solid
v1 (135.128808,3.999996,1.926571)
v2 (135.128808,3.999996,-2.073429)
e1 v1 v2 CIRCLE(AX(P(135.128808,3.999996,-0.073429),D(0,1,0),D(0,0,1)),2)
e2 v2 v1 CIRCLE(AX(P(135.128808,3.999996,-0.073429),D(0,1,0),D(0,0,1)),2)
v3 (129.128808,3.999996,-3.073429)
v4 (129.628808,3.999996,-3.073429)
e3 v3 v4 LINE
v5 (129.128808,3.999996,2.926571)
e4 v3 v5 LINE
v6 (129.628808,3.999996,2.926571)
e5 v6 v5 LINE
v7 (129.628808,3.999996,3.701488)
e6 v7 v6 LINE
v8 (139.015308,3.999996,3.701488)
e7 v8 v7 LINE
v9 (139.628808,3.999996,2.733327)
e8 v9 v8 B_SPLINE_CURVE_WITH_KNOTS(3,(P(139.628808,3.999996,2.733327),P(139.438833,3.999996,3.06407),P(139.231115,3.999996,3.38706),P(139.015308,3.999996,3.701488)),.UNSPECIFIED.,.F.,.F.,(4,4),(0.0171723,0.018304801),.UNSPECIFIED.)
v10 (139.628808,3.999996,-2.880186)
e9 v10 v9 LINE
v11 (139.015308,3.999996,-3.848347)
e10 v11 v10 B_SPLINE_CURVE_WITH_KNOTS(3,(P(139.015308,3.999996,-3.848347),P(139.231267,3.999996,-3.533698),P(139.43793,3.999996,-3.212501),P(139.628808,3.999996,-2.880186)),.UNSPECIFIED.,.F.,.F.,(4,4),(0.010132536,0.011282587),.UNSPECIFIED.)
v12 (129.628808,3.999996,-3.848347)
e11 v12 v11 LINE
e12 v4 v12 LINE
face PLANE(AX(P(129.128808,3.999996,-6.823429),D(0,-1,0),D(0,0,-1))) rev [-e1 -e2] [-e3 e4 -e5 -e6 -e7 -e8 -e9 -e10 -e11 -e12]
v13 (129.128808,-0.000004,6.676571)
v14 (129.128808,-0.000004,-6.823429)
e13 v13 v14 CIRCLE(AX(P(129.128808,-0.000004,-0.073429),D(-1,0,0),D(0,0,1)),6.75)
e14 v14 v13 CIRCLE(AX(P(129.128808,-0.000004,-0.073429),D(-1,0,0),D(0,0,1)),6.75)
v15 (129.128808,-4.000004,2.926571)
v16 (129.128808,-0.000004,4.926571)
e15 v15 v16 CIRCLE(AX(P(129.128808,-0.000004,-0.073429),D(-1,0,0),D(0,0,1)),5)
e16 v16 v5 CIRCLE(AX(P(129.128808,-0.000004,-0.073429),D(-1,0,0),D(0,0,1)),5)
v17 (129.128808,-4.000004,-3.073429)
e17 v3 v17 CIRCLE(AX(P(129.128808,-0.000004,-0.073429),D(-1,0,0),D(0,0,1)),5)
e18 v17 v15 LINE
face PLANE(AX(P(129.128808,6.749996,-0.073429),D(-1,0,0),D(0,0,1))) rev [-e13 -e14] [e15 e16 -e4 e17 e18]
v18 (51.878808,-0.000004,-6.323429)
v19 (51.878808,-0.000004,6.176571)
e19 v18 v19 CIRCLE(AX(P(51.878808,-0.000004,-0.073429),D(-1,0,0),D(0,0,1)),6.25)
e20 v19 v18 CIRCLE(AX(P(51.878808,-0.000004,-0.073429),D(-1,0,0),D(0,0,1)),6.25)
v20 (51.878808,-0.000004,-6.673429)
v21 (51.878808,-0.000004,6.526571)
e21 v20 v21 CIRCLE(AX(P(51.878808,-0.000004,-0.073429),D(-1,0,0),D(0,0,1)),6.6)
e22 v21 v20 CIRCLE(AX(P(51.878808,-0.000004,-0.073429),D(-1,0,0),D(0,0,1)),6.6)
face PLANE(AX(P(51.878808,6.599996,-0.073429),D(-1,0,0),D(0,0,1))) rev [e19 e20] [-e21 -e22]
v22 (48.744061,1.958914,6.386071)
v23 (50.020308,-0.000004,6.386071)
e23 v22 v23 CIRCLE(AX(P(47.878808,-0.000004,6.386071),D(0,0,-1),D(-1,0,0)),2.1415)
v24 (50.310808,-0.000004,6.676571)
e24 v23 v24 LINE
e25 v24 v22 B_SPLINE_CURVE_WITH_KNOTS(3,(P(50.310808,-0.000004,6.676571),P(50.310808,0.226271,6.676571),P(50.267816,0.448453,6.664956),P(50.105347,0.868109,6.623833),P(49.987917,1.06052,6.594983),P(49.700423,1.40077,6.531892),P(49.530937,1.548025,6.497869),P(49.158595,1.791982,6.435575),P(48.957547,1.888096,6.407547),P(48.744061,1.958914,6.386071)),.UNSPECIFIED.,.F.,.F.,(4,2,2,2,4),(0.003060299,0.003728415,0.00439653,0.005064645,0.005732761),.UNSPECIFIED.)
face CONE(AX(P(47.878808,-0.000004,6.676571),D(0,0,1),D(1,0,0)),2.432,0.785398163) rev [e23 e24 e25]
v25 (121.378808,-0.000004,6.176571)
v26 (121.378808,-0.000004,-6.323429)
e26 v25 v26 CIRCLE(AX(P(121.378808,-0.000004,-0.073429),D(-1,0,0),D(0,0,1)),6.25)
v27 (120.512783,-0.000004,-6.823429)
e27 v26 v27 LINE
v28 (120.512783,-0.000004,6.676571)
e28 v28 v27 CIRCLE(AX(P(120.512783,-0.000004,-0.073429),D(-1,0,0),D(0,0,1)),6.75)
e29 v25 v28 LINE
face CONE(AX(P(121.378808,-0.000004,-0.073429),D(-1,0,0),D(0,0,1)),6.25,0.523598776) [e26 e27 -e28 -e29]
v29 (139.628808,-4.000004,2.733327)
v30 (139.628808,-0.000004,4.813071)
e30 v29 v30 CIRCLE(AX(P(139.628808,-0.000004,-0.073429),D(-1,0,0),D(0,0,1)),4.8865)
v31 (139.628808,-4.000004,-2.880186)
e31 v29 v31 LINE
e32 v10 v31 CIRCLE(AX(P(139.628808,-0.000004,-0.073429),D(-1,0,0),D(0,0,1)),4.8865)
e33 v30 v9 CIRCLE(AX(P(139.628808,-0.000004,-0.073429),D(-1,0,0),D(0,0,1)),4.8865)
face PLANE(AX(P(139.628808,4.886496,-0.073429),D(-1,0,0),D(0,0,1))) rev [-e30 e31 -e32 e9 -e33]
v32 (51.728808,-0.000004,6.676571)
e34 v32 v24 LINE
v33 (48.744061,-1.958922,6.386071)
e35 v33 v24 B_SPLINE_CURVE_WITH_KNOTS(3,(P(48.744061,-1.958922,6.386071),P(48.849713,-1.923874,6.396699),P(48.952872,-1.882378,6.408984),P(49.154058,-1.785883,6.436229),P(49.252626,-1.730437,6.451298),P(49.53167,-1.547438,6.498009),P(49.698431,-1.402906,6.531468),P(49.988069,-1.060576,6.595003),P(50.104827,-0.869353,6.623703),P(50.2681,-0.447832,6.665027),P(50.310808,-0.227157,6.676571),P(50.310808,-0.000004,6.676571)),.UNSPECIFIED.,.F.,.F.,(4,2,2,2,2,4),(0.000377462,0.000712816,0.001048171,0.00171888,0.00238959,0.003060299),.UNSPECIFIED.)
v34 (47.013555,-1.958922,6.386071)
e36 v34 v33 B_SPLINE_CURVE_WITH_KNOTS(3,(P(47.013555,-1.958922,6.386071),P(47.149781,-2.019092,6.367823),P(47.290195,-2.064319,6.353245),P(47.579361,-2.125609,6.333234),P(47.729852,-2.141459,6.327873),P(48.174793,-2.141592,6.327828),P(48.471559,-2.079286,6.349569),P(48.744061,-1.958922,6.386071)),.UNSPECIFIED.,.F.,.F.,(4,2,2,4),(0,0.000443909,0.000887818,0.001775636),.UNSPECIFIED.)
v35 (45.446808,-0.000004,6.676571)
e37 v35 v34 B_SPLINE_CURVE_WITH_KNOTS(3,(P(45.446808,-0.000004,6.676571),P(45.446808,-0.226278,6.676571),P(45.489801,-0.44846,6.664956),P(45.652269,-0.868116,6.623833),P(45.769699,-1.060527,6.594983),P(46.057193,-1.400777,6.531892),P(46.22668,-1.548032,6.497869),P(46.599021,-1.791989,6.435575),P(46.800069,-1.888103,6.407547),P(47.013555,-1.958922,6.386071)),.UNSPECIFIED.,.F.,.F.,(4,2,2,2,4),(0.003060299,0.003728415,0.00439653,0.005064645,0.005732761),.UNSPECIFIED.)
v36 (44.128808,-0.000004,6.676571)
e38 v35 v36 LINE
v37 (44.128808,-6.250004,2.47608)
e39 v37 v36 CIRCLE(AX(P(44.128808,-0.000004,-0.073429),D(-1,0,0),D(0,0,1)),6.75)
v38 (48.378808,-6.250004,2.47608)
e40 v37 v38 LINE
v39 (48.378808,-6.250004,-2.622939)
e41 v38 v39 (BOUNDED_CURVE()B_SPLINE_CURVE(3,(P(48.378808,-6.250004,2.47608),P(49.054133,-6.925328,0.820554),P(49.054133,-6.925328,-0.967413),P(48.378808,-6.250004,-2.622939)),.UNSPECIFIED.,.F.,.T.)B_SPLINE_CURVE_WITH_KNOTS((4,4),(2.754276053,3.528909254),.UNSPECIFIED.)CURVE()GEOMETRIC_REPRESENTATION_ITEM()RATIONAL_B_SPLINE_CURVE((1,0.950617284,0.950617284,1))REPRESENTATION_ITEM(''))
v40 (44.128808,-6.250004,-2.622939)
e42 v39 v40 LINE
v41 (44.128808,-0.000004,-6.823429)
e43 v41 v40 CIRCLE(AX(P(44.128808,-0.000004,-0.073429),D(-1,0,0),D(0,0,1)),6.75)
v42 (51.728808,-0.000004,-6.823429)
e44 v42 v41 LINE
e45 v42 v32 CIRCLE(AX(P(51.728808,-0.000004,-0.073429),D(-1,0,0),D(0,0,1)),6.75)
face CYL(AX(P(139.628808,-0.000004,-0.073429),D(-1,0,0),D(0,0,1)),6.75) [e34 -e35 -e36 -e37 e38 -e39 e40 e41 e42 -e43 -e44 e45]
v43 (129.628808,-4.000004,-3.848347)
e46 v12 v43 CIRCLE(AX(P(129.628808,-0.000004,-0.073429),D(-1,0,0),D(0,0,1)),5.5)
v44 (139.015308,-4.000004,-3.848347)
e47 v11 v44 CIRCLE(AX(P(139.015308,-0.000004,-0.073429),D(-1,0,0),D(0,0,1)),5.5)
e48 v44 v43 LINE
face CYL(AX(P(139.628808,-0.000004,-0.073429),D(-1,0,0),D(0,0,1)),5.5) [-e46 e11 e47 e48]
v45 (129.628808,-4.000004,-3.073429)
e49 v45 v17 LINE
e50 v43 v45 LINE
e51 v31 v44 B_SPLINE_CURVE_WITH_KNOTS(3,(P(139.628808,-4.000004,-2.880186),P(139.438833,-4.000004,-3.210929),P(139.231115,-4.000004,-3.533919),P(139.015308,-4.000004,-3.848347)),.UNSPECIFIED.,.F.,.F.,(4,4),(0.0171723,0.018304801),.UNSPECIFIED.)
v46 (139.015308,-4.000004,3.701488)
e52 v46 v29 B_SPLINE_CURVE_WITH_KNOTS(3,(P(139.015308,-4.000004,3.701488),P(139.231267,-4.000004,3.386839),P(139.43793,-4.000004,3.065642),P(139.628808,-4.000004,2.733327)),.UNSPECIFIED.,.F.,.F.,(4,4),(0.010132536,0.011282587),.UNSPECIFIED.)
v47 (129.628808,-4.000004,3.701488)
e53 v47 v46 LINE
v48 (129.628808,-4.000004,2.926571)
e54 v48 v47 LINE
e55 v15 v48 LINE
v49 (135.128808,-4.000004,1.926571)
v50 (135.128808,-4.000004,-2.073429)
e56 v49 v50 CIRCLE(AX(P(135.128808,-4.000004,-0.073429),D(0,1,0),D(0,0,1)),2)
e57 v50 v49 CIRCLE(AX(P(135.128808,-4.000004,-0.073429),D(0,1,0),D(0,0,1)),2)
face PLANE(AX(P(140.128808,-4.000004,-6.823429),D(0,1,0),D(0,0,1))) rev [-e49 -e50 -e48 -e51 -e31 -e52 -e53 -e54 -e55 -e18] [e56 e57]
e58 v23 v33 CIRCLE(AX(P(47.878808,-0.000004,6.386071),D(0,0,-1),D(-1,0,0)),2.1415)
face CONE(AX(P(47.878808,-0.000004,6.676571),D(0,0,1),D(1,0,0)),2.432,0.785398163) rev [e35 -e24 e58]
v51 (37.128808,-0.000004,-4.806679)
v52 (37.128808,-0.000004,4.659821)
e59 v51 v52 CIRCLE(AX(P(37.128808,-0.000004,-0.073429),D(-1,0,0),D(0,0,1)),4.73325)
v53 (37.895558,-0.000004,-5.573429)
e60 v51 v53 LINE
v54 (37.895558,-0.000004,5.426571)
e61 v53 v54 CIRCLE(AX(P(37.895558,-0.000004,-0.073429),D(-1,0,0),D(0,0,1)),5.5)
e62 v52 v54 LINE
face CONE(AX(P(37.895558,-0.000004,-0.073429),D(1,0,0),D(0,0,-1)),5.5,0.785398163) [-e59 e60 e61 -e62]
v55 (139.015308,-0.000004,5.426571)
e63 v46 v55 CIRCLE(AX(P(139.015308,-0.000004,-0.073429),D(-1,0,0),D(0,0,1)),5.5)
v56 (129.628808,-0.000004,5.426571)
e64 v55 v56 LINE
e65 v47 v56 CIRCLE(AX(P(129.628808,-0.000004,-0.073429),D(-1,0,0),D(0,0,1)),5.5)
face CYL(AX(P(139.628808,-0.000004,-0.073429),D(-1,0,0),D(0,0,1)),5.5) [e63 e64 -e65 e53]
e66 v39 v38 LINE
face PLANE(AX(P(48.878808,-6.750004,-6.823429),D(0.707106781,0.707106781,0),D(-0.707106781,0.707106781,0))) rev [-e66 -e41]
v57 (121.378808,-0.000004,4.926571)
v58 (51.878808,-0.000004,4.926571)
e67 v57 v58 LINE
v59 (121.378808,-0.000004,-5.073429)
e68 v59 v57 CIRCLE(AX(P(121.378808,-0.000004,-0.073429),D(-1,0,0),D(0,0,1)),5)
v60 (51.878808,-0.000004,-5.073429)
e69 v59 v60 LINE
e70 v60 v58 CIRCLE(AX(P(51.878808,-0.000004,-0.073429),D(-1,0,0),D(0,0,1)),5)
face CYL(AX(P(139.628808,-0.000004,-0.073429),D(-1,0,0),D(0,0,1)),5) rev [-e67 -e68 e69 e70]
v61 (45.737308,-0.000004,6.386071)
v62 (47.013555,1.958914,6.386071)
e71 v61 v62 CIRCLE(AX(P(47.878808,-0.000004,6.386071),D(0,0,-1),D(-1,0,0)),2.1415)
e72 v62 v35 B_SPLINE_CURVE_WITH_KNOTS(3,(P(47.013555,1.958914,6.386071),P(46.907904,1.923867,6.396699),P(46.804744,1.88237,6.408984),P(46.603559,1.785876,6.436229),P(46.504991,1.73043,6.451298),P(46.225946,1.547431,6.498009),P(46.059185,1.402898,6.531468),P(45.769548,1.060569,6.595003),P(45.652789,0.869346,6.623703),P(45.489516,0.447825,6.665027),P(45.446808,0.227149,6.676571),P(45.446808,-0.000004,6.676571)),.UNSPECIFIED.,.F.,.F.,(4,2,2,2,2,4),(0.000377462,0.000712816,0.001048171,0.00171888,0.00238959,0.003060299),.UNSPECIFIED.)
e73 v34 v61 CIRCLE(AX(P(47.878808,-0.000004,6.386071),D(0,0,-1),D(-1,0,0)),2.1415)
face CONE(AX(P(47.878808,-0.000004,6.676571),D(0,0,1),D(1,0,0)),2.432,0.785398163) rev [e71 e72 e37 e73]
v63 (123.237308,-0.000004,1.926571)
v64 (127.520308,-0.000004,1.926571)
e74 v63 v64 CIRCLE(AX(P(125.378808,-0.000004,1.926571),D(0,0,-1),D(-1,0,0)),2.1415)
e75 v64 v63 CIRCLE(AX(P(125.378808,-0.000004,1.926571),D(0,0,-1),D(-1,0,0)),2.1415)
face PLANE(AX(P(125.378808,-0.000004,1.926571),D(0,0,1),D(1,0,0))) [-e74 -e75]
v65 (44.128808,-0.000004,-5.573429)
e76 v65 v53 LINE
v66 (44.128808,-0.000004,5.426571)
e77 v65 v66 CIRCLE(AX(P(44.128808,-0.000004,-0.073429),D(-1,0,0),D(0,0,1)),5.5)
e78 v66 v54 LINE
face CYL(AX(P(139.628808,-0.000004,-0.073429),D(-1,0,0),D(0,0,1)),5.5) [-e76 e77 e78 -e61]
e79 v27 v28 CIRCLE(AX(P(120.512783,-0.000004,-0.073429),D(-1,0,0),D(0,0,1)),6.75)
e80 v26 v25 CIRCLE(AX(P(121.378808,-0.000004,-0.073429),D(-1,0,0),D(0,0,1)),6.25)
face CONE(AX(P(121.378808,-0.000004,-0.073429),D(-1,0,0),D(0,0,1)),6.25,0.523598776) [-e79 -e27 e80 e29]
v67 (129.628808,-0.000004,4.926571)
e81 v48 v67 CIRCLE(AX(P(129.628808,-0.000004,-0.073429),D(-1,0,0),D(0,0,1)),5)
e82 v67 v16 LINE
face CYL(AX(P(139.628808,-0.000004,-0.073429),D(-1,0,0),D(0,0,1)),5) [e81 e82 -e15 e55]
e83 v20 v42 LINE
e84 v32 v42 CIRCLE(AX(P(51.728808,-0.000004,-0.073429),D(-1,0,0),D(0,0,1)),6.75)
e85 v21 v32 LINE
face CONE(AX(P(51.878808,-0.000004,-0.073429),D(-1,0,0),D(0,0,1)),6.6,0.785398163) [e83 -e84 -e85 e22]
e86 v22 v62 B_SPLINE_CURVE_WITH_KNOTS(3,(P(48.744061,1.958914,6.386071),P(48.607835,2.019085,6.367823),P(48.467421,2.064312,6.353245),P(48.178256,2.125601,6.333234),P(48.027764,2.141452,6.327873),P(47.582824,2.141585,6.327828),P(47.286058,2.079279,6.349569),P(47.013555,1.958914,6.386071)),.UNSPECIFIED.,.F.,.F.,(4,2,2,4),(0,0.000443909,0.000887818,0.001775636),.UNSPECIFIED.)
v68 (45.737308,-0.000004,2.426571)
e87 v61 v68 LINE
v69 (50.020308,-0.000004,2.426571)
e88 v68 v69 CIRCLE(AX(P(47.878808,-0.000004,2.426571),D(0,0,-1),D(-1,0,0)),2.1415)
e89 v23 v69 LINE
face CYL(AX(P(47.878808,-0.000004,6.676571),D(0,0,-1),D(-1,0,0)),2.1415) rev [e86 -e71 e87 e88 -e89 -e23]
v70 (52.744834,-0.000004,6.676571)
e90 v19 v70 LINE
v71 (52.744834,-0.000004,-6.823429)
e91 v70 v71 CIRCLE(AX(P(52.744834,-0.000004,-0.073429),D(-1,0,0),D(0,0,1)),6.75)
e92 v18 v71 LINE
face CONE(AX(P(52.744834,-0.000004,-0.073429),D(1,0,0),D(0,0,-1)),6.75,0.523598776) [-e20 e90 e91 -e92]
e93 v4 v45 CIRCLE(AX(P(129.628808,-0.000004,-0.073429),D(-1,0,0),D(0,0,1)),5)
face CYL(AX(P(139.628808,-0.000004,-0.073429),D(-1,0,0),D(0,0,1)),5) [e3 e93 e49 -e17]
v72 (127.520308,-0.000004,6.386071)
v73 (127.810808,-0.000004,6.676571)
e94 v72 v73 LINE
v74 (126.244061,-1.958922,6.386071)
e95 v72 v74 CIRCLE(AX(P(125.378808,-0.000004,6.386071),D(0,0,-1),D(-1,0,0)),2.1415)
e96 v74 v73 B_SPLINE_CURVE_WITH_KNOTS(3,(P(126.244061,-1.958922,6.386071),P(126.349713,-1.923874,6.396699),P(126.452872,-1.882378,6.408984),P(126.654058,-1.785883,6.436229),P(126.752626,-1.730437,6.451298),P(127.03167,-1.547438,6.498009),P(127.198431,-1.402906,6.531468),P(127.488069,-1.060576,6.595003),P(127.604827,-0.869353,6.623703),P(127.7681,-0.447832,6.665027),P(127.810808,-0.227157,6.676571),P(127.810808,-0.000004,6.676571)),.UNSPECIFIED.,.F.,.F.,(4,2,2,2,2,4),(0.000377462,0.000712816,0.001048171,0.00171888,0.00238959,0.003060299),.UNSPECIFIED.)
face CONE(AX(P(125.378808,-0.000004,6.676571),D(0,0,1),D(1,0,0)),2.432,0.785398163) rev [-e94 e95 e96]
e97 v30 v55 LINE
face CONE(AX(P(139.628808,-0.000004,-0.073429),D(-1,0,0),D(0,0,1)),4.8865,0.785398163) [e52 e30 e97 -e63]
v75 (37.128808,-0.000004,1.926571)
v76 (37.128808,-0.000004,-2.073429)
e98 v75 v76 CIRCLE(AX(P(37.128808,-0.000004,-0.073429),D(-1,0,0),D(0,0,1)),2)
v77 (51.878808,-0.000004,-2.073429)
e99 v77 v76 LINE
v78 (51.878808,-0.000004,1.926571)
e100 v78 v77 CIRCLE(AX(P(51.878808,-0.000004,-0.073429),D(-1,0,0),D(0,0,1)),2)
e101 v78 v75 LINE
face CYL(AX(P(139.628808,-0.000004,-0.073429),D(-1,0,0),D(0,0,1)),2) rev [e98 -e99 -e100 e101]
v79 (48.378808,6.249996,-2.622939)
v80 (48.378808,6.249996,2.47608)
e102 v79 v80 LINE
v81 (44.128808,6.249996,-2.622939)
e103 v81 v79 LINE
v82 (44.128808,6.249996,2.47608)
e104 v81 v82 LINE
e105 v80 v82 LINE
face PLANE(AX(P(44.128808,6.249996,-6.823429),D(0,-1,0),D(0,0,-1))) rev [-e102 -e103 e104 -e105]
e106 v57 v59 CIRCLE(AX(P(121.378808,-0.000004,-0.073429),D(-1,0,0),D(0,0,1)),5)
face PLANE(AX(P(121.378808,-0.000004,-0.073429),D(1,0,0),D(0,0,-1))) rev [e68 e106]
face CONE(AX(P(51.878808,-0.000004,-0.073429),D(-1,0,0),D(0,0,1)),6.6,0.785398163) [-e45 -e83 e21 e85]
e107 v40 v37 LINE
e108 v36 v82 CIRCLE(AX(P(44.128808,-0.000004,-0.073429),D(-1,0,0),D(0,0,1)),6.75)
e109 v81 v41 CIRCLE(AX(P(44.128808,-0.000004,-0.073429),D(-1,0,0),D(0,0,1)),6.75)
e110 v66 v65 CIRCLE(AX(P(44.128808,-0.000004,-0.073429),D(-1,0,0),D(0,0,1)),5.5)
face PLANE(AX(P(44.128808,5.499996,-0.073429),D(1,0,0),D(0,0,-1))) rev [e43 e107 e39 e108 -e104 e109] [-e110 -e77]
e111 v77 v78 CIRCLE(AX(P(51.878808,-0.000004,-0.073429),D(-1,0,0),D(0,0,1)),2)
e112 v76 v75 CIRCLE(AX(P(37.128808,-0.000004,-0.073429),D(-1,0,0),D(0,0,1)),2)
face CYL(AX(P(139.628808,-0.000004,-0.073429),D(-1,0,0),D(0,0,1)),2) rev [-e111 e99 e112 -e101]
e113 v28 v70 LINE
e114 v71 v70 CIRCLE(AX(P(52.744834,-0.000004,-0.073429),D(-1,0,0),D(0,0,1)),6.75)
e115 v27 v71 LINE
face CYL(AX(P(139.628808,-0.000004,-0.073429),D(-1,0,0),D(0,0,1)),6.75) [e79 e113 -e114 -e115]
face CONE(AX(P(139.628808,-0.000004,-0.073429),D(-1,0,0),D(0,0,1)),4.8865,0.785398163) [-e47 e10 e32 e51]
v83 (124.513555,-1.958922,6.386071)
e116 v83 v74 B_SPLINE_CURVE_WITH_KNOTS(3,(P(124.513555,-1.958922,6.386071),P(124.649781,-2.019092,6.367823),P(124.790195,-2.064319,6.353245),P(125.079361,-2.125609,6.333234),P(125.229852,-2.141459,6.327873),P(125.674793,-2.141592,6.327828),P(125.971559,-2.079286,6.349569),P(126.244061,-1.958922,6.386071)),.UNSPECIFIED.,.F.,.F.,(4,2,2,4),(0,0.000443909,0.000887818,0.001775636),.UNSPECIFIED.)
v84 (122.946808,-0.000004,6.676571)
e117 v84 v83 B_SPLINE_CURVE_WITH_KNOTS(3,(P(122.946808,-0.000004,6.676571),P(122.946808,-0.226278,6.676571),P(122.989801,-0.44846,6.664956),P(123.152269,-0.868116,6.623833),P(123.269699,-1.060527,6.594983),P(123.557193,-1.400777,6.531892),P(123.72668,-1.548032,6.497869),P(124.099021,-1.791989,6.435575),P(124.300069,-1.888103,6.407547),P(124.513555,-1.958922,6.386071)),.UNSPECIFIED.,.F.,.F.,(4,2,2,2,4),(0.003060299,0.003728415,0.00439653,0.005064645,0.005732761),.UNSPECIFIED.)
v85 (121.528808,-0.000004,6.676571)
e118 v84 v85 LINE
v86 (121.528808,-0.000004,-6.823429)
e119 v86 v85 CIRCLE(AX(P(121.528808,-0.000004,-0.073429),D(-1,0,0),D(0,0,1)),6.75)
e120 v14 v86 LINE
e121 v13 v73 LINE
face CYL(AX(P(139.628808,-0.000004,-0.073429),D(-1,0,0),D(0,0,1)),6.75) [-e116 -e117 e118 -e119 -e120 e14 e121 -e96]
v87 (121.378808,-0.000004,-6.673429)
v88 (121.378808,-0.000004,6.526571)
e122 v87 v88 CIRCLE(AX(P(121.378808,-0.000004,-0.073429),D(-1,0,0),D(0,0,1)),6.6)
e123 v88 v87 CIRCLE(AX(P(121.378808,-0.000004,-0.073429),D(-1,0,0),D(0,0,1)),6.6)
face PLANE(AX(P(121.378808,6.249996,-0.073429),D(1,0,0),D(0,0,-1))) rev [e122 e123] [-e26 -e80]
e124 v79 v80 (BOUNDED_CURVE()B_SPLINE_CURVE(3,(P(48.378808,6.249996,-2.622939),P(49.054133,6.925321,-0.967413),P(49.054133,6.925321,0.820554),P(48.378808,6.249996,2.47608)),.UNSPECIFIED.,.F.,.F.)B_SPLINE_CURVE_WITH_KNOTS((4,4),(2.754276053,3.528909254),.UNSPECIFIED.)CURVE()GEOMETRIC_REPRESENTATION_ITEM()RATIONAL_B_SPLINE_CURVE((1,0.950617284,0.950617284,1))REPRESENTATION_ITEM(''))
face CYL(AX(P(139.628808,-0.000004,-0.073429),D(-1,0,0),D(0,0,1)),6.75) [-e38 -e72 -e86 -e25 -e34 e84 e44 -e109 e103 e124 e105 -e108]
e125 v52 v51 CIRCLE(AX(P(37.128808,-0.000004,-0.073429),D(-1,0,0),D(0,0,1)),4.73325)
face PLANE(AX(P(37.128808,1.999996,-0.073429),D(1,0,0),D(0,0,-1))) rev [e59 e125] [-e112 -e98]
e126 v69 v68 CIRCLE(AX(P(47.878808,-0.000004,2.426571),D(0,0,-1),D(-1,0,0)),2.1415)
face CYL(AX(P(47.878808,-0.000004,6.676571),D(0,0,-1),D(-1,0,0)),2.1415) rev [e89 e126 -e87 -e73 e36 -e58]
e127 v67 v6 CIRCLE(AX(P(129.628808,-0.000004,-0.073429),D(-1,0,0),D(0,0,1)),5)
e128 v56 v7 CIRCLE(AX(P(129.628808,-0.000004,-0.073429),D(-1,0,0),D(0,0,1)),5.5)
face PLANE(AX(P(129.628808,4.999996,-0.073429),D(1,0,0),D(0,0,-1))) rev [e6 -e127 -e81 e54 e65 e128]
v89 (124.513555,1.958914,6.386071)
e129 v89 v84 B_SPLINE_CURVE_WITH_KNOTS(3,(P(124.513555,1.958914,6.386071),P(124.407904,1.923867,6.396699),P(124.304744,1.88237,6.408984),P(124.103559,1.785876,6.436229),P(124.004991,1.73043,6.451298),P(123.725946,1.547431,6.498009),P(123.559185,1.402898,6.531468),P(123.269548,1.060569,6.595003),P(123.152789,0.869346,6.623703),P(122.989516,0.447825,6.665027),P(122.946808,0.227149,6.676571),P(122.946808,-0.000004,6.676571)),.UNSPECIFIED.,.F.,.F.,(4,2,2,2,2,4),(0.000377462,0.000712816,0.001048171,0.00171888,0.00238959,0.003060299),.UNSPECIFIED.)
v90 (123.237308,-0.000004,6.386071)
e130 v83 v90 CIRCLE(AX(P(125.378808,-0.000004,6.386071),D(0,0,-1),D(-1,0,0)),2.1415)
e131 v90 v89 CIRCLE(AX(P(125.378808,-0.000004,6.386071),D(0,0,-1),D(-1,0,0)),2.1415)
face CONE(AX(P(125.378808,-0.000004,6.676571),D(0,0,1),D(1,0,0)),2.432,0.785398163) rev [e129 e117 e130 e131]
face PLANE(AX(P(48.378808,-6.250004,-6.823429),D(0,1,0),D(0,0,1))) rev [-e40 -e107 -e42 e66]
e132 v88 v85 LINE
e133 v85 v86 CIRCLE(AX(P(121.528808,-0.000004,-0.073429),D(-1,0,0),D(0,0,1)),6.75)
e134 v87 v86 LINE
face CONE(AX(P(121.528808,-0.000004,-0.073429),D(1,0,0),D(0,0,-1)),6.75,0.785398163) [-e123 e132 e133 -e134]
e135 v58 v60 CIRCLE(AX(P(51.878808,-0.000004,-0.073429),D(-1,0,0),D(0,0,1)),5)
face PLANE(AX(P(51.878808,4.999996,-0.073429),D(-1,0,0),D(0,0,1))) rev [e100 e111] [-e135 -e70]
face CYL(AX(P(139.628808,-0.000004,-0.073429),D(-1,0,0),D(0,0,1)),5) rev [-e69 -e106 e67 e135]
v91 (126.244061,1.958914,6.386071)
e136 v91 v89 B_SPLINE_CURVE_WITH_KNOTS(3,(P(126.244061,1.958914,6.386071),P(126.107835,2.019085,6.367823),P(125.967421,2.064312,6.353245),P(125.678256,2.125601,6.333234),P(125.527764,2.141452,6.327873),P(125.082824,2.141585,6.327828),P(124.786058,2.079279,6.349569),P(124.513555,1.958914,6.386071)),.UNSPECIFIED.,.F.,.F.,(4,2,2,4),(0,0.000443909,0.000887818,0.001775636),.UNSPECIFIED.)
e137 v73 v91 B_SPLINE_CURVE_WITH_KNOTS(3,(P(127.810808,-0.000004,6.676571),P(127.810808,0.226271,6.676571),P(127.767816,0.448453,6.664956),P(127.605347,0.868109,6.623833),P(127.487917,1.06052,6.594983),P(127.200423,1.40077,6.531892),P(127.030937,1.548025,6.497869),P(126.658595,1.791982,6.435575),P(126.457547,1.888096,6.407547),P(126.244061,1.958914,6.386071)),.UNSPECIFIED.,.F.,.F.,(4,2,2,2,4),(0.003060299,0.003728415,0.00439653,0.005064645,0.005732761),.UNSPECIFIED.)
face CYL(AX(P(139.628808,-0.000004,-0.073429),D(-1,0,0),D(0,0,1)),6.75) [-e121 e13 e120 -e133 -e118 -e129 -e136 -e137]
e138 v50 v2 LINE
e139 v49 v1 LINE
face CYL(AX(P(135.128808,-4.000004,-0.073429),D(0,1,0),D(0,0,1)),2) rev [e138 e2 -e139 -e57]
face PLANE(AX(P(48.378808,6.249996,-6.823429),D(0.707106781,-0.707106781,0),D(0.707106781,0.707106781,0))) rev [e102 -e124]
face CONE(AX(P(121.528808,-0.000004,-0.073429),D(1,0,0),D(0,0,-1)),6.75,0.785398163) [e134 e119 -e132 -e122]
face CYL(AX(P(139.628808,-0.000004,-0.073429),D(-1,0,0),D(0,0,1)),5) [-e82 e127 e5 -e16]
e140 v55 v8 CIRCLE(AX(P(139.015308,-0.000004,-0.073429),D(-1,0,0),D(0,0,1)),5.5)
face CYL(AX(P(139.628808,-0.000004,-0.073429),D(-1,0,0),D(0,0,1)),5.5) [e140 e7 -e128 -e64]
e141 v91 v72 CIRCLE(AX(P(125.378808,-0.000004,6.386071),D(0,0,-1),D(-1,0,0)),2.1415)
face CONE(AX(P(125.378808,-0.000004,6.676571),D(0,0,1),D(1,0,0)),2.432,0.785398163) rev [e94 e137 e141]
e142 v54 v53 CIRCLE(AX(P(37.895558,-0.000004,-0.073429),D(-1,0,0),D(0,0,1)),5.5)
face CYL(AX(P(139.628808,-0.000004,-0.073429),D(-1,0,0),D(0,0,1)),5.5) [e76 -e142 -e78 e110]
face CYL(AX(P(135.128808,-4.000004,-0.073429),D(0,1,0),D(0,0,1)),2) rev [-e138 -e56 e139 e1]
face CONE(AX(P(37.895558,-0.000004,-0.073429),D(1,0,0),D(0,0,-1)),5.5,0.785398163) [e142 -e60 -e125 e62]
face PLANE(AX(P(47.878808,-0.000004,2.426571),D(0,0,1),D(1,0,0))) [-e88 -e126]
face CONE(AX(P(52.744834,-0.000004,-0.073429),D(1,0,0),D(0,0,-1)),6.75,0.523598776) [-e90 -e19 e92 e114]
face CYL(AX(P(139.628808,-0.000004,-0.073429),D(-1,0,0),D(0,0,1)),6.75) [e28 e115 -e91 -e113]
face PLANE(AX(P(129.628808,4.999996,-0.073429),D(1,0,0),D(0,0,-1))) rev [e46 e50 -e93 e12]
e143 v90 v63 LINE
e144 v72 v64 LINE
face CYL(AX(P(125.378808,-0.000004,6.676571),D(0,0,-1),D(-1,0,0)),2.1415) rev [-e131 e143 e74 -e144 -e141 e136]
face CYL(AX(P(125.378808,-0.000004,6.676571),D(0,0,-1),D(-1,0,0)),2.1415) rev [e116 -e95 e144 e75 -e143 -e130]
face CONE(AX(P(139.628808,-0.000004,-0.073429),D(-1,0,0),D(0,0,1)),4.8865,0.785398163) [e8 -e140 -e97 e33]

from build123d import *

# Parameters (mm, degrees)
CUT_EXTRUDE_1_DEPTH      = 13.5
CUT_EXTRUDE_1_DEPTH_BACK = 13.5
CUT_EXTRUDE_2_DEPTH      = 13.5
CUT_EXTRUDE_2_DEPTH_BACK = 13.5
CUT_EXTRUDE_3_DEPTH      = 13.5
CUT_EXTRUDE_3_DEPTH_BACK = 13.5
CUT_EXTRUDE_4_DEPTH      = 8
CUT_EXTRUDE_4_DEPTH_BACK = 8
SKETCH_5_R               = 4
SCALE_1_SCALE            = 0.5


with BuildPart() as part:
    # 草图1 → 旋转1 (revolve)
    with BuildSketch(Plane.XY, mode=Mode.PRIVATE) as revolve_1_sk:
        Polygon((154.5, 0), (154.5, 10), (15.5, 10), (15.5, 4), (-14, 4), (-14, 9.4665), (-12.4665, 11), (0, 11), (0, 13.5), (15.2, 13.5), (15.5, 13.2), (15.5, 12.5), (17.232050808, 13.5), (152.767949192, 13.5), (154.5, 12.5), (154.5, 13.2), (154.8, 13.5), (170, 13.5), (170, 10), (171, 10), (171, 11), (189.773, 11), (191, 9.773), (191, 0), align=None)
    revolve(revolve_1_sk.sketch.rotate(Axis((191, 0, 0), (-1, 0, 0)), 270), axis=Axis((191, 0, 0), (-1, 0, 0)))

    # 草图2 → 切除-拉伸1 (cut, two sides: drawn at the far end of the back side and taken through both)
    with BuildSketch(Plane.XY.offset(-CUT_EXTRUDE_1_DEPTH_BACK)):
        Polygon((0, 13.5), (0, 12.5), (8.5, 12.5), (9.5, 13.5), align=None)
    extrude(amount=CUT_EXTRUDE_1_DEPTH + CUT_EXTRUDE_1_DEPTH_BACK, mode=Mode.SUBTRACT)

    # 草图3 → 切除-拉伸2 (cut, two sides: drawn at the far end of the back side and taken through both)
    with BuildSketch(Plane.XY.offset(-CUT_EXTRUDE_2_DEPTH_BACK)):
        Polygon((0, -13.5), (9.5, -13.5), (8.5, -12.5), (0, -12.5), align=None)
    extrude(amount=CUT_EXTRUDE_2_DEPTH + CUT_EXTRUDE_2_DEPTH_BACK, mode=Mode.SUBTRACT)

    # 草图4 → 切除-拉伸3 (cut, two sides: drawn at the far end of the back side and taken through both)
    with BuildSketch(Plane.XY.offset(-CUT_EXTRUDE_3_DEPTH_BACK)):
        Polygon((170, 23), (170, 8), (192, 8), (192, -8), (170, -8), (170, -23), (197, -23), (197, 23), align=None)
    extrude(amount=CUT_EXTRUDE_3_DEPTH + CUT_EXTRUDE_3_DEPTH_BACK, mode=Mode.SUBTRACT)

    # 草图5 → 切除-拉伸4 (cut, two sides: drawn at the far end of the back side and taken through both)
    with BuildSketch(Plane(origin=(0, 0, 0), x_dir=(1, 0, 0), z_dir=(0, 1, 0)).offset(-CUT_EXTRUDE_4_DEPTH_BACK)):
        with Locations(Location((182, 0, 0), (0, 0, 270))):
            Circle(SKETCH_5_R)
    extrude(amount=CUT_EXTRUDE_4_DEPTH + CUT_EXTRUDE_4_DEPTH_BACK, mode=Mode.SUBTRACT)

    # 草图6 → 切除-旋转1 (revolve, cut)
    with BuildSketch(Plane(origin=(0, 0, 0), x_dir=(1, 0, 0), z_dir=(0, 1, 0)), mode=Mode.PRIVATE) as cut_revolve_1_sk:
        Polygon((7.5, -5), (11.783, -5), (11.783, -12.919), (12.364, -13.5), (7.5, -13.5), align=None)
    revolve(cut_revolve_1_sk.sketch.rotate(Axis((7.5, 0, 13.5), (0, 0, -1)), 180), axis=Axis((7.5, 0, 13.5), (0, 0, -1)), mode=Mode.SUBTRACT)

    # 草图7 → 切除-旋转2 (revolve, cut)
    with BuildSketch(Plane(origin=(0, 0, 0), x_dir=(1, 0, 0), z_dir=(0, 1, 0)), mode=Mode.PRIVATE) as cut_revolve_2_sk:
        Polygon((162.5, -4), (166.783, -4), (166.783, -12.919), (167.364, -13.5), (162.5, -13.5), align=None)
    revolve(cut_revolve_2_sk.sketch.rotate(Axis((162.5, 0, 13.5), (0, 0, -1)), 180), axis=Axis((162.5, 0, 13.5), (0, 0, -1)), mode=Mode.SUBTRACT)


with BuildPart() as part_1:
    # 缩放比例1: scaled about (88.257573556, -1e-09, -0.146875551)
    add(part.part.scale(SCALE_1_SCALE).moved(Location((44.128786778, -1e-09, -0.073437775))))


solid = part_1.part
